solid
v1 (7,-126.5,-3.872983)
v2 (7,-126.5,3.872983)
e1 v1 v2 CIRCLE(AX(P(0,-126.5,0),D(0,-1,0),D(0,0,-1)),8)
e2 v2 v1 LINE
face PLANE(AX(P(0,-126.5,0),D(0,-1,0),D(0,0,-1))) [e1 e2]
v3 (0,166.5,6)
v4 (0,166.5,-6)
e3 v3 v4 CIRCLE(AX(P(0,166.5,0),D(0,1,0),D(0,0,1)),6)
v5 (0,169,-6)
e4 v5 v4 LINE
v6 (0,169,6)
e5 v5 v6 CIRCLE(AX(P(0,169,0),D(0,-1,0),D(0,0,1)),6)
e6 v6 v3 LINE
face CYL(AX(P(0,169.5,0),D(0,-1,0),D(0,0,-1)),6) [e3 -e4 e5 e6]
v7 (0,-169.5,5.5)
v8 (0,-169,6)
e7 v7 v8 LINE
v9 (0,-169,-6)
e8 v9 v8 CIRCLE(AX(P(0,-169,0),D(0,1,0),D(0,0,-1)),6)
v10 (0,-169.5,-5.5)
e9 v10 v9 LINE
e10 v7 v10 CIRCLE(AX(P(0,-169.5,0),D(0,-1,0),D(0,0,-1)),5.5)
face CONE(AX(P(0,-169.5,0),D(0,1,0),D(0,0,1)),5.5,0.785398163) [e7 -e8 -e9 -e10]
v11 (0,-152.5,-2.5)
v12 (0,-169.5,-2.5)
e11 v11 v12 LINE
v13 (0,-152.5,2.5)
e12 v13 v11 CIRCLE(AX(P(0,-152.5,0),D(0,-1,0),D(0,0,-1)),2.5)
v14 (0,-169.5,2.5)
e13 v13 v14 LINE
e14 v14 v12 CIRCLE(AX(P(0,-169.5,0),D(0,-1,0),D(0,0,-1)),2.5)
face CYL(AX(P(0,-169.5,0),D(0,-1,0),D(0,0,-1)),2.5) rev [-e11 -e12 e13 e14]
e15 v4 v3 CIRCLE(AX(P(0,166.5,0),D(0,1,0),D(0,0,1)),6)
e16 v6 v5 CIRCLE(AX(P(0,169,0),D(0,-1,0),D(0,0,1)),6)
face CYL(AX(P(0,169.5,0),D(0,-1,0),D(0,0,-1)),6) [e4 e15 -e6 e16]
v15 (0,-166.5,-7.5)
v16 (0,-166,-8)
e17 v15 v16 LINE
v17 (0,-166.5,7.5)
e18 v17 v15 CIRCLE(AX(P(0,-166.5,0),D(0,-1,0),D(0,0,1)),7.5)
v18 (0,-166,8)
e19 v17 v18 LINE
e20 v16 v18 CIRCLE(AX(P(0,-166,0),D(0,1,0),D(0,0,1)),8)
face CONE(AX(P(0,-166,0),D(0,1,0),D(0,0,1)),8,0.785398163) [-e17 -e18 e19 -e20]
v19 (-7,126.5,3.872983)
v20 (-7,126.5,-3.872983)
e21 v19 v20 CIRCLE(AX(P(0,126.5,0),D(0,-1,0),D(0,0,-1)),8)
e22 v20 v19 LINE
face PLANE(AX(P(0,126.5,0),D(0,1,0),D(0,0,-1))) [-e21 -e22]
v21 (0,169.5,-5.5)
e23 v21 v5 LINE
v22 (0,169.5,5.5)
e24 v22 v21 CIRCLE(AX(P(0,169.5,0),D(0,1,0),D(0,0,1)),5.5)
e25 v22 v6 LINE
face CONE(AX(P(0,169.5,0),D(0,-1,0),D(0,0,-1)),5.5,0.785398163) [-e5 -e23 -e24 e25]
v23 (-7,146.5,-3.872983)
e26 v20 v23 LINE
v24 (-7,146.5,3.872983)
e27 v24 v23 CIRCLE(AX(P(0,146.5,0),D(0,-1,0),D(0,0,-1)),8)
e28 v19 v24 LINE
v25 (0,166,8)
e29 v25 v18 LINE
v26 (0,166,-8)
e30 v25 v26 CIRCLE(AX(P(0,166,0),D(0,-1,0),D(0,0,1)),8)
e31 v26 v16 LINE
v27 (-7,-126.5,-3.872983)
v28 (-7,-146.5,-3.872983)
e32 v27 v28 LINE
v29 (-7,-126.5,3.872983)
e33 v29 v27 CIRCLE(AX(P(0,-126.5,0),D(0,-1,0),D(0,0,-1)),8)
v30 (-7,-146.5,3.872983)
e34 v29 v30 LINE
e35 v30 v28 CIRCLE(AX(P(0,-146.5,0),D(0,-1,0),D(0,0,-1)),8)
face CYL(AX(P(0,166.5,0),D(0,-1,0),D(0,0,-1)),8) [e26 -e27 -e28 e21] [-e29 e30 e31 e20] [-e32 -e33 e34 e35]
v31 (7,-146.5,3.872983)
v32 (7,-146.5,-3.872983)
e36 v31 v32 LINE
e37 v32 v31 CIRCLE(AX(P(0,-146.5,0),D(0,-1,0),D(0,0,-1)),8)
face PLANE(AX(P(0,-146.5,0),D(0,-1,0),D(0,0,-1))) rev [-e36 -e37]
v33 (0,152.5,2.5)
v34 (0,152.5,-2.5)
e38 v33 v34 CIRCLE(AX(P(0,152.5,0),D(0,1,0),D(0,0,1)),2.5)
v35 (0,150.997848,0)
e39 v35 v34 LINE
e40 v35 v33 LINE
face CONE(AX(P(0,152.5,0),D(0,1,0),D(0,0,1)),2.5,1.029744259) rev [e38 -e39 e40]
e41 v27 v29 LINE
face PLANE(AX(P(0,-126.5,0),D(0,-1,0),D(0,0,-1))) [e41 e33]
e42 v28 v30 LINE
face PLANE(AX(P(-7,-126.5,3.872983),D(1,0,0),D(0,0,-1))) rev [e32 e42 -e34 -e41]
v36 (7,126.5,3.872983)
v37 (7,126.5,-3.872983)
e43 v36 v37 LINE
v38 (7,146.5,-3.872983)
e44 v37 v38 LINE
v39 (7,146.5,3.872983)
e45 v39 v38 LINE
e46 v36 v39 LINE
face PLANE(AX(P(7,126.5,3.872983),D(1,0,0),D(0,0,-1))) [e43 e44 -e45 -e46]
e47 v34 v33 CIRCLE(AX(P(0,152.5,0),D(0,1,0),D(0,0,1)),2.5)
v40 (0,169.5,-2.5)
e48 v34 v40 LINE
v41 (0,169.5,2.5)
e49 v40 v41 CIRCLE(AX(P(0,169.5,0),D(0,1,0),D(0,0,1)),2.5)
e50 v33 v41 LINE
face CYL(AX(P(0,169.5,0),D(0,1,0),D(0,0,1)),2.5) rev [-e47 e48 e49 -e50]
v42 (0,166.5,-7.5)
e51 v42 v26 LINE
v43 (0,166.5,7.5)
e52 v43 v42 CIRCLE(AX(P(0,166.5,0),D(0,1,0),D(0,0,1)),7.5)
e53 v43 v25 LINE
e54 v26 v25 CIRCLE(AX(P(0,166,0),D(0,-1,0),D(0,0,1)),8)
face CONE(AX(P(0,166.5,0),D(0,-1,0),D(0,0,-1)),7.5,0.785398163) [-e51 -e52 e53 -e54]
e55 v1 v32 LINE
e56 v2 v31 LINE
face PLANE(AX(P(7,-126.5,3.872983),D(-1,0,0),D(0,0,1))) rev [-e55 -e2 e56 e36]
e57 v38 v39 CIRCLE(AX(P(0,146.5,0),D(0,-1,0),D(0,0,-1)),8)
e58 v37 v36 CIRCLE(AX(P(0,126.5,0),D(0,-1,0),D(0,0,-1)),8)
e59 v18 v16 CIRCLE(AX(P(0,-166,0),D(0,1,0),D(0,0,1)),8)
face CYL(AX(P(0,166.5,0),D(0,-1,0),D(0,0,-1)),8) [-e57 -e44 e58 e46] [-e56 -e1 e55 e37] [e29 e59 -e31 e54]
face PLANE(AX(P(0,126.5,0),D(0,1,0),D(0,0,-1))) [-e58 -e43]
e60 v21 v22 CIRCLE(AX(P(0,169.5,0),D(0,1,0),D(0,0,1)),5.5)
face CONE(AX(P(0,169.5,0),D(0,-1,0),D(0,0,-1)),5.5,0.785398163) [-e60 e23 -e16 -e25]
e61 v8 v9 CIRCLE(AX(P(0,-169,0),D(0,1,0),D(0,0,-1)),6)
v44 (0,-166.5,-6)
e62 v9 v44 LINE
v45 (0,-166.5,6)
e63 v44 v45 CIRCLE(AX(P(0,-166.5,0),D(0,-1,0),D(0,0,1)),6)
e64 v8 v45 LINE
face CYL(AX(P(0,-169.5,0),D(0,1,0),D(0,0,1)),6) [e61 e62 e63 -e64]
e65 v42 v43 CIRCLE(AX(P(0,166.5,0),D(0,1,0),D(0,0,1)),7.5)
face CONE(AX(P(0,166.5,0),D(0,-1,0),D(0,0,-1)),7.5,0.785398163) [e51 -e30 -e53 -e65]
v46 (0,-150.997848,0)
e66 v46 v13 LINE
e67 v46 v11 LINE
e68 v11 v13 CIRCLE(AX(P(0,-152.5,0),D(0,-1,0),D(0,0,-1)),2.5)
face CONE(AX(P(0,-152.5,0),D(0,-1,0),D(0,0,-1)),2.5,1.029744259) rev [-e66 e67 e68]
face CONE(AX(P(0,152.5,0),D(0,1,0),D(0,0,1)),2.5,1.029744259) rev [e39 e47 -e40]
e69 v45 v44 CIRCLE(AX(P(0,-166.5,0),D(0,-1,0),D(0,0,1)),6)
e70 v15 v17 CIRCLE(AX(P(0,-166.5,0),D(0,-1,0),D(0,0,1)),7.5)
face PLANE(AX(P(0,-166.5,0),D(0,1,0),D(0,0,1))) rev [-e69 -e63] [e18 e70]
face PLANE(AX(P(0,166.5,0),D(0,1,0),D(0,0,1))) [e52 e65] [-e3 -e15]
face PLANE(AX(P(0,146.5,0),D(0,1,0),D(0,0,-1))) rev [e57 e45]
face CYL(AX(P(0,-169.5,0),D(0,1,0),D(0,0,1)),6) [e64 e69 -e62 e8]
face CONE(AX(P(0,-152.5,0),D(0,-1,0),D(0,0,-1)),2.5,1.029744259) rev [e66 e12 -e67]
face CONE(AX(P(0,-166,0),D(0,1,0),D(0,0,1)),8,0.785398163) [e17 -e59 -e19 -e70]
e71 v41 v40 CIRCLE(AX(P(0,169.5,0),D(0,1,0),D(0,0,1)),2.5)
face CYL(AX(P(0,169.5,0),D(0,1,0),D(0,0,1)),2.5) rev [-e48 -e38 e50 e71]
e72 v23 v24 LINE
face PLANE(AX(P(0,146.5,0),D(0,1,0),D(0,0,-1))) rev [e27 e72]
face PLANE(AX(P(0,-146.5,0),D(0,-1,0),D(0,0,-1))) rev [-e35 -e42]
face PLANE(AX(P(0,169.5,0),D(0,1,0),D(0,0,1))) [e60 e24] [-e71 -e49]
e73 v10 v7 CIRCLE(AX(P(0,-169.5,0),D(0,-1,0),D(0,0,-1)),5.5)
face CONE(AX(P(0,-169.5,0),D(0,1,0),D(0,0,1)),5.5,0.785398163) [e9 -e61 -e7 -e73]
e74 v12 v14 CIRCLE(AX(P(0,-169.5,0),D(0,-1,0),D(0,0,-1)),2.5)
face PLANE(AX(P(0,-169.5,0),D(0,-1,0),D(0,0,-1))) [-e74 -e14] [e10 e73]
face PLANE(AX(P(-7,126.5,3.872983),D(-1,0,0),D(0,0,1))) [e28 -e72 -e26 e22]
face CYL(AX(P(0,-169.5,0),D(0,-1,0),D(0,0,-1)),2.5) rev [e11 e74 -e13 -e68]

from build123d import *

# Parameters (mm, degrees)
SKETCH1_R             = 8
BOSS_EXTRUDE1_DEPTH   = 166.5
SKETCH2_R             = 6
BOSS_EXTRUDE2_DEPTH   = 3
CHAMFER1_SIZE         = 0.5
CUT_EXTRUDE2_START    = -40
CUT_EXTRUDE2_DEPTH    = 20
M6_TAPPED_HOLE1_D     = 5
M6_TAPPED_HOLE1_DEPTH = 17
M6_TAPPED_HOLE1_TIP   = 1.502151548
CHAMFER2_SIZE         = 0.5
BOSS_EXTRUDE3_START   = 3
SKETCH6_R             = 6
BOSS_EXTRUDE3_DEPTH   = 3
CHAMFER3_SIZE         = 0.5
M6_TAPPED_HOLE2_D     = 5
M6_TAPPED_HOLE2_DEPTH = 17
M6_TAPPED_HOLE2_TIP   = 1.502151548


with BuildPart() as part:
    # Sketch1 → Boss-Extrude1 (new, symmetric)
    with BuildSketch(Plane(origin=(0, 0, 0), x_dir=(1, 0, 0), z_dir=(0, 1, 0))):
        with Locations(Location((0, 0, 0), (0, 0, 270))):
            Circle(SKETCH1_R)
    extrude(amount=BOSS_EXTRUDE1_DEPTH, both=True)

    # Sketch2 → Boss-Extrude2 (add)
    with BuildSketch(Plane.XZ.offset(166.5)):
        with Locations(Location((0, 0, 0), (0, 0, 90))):
            Circle(SKETCH2_R)
    extrude(amount=BOSS_EXTRUDE2_DEPTH)

    # Chamfer1
    chamfer1_edges = [part.edges().sort_by_distance(p)[0] for p in [
        (0, -166.5, -8),
        (0, -169.5, -6),
    ]]
    chamfer(chamfer1_edges, length=CHAMFER1_SIZE)

    # Sketch3 → Cut-Extrude2 (cut)
    with BuildSketch(Plane.XZ.offset(166.5).offset(CUT_EXTRUDE2_START)):
        with BuildLine():
            Line((-7, 3.872983346), (-7, -3.872983346))
            ThreePointArc((-7, -3.872983346), (-8, 0), (-7, 3.872983346))
        make_face()
        with BuildLine():
            Line((7, 3.872983346), (7, -3.872983346))
            ThreePointArc((7, -3.872983346), (8, 0), (7, 3.872983346))
        make_face()
    cut_extrude2 = extrude(amount=CUT_EXTRUDE2_DEPTH, mode=Mode.SUBTRACT)

    # M6 Tapped Hole1
    with Locations(Plane.XZ.offset(169.5)):
        with Locations((0, 0)):
            Hole(M6_TAPPED_HOLE1_D / 2, depth=M6_TAPPED_HOLE1_DEPTH)
            with Locations((0, 0, -(M6_TAPPED_HOLE1_DEPTH + M6_TAPPED_HOLE1_TIP / 2))):  # 118° drill point
                Cone(0, M6_TAPPED_HOLE1_D / 2, M6_TAPPED_HOLE1_TIP, mode=Mode.SUBTRACT)

    # Chamfer2
    chamfer2_edges = [part.edges().sort_by_distance(p)[0] for p in [
        (0, 166.5, -8),
    ]]
    chamfer(chamfer2_edges, length=CHAMFER2_SIZE)

    # Sketch6 → Boss-Extrude3 (add)
    with BuildSketch(Plane(origin=(0, 166.5, 0), x_dir=(1, 0, 0), z_dir=(0, 1, 0)).offset(BOSS_EXTRUDE3_START)):
        with Locations(Location((0, 0, 0), (0, 0, 270))):
            Circle(SKETCH6_R)
    extrude(amount=-BOSS_EXTRUDE3_DEPTH)

    # Chamfer3
    chamfer3_edges = [part.edges().sort_by_distance(p)[0] for p in [
        (0, 169.5, -6),
    ]]
    chamfer(chamfer3_edges, length=CHAMFER3_SIZE)

    # M6 Tapped Hole2
    with Locations(Plane(origin=(0, 169.5, 0), x_dir=(-1, 0, 0), z_dir=(0, 1, 0))):
        with Locations((0, 0)):
            Hole(M6_TAPPED_HOLE2_D / 2, depth=M6_TAPPED_HOLE2_DEPTH)
            with Locations((0, 0, -(M6_TAPPED_HOLE2_DEPTH + M6_TAPPED_HOLE2_TIP / 2))):  # 118° drill point
                Cone(0, M6_TAPPED_HOLE2_D / 2, M6_TAPPED_HOLE2_TIP, mode=Mode.SUBTRACT)

    # Mirror1: Cut-Extrude2 across plane
    add(cut_extrude2.mirror(Plane.ZX), mode=Mode.SUBTRACT)


solid = part.part
